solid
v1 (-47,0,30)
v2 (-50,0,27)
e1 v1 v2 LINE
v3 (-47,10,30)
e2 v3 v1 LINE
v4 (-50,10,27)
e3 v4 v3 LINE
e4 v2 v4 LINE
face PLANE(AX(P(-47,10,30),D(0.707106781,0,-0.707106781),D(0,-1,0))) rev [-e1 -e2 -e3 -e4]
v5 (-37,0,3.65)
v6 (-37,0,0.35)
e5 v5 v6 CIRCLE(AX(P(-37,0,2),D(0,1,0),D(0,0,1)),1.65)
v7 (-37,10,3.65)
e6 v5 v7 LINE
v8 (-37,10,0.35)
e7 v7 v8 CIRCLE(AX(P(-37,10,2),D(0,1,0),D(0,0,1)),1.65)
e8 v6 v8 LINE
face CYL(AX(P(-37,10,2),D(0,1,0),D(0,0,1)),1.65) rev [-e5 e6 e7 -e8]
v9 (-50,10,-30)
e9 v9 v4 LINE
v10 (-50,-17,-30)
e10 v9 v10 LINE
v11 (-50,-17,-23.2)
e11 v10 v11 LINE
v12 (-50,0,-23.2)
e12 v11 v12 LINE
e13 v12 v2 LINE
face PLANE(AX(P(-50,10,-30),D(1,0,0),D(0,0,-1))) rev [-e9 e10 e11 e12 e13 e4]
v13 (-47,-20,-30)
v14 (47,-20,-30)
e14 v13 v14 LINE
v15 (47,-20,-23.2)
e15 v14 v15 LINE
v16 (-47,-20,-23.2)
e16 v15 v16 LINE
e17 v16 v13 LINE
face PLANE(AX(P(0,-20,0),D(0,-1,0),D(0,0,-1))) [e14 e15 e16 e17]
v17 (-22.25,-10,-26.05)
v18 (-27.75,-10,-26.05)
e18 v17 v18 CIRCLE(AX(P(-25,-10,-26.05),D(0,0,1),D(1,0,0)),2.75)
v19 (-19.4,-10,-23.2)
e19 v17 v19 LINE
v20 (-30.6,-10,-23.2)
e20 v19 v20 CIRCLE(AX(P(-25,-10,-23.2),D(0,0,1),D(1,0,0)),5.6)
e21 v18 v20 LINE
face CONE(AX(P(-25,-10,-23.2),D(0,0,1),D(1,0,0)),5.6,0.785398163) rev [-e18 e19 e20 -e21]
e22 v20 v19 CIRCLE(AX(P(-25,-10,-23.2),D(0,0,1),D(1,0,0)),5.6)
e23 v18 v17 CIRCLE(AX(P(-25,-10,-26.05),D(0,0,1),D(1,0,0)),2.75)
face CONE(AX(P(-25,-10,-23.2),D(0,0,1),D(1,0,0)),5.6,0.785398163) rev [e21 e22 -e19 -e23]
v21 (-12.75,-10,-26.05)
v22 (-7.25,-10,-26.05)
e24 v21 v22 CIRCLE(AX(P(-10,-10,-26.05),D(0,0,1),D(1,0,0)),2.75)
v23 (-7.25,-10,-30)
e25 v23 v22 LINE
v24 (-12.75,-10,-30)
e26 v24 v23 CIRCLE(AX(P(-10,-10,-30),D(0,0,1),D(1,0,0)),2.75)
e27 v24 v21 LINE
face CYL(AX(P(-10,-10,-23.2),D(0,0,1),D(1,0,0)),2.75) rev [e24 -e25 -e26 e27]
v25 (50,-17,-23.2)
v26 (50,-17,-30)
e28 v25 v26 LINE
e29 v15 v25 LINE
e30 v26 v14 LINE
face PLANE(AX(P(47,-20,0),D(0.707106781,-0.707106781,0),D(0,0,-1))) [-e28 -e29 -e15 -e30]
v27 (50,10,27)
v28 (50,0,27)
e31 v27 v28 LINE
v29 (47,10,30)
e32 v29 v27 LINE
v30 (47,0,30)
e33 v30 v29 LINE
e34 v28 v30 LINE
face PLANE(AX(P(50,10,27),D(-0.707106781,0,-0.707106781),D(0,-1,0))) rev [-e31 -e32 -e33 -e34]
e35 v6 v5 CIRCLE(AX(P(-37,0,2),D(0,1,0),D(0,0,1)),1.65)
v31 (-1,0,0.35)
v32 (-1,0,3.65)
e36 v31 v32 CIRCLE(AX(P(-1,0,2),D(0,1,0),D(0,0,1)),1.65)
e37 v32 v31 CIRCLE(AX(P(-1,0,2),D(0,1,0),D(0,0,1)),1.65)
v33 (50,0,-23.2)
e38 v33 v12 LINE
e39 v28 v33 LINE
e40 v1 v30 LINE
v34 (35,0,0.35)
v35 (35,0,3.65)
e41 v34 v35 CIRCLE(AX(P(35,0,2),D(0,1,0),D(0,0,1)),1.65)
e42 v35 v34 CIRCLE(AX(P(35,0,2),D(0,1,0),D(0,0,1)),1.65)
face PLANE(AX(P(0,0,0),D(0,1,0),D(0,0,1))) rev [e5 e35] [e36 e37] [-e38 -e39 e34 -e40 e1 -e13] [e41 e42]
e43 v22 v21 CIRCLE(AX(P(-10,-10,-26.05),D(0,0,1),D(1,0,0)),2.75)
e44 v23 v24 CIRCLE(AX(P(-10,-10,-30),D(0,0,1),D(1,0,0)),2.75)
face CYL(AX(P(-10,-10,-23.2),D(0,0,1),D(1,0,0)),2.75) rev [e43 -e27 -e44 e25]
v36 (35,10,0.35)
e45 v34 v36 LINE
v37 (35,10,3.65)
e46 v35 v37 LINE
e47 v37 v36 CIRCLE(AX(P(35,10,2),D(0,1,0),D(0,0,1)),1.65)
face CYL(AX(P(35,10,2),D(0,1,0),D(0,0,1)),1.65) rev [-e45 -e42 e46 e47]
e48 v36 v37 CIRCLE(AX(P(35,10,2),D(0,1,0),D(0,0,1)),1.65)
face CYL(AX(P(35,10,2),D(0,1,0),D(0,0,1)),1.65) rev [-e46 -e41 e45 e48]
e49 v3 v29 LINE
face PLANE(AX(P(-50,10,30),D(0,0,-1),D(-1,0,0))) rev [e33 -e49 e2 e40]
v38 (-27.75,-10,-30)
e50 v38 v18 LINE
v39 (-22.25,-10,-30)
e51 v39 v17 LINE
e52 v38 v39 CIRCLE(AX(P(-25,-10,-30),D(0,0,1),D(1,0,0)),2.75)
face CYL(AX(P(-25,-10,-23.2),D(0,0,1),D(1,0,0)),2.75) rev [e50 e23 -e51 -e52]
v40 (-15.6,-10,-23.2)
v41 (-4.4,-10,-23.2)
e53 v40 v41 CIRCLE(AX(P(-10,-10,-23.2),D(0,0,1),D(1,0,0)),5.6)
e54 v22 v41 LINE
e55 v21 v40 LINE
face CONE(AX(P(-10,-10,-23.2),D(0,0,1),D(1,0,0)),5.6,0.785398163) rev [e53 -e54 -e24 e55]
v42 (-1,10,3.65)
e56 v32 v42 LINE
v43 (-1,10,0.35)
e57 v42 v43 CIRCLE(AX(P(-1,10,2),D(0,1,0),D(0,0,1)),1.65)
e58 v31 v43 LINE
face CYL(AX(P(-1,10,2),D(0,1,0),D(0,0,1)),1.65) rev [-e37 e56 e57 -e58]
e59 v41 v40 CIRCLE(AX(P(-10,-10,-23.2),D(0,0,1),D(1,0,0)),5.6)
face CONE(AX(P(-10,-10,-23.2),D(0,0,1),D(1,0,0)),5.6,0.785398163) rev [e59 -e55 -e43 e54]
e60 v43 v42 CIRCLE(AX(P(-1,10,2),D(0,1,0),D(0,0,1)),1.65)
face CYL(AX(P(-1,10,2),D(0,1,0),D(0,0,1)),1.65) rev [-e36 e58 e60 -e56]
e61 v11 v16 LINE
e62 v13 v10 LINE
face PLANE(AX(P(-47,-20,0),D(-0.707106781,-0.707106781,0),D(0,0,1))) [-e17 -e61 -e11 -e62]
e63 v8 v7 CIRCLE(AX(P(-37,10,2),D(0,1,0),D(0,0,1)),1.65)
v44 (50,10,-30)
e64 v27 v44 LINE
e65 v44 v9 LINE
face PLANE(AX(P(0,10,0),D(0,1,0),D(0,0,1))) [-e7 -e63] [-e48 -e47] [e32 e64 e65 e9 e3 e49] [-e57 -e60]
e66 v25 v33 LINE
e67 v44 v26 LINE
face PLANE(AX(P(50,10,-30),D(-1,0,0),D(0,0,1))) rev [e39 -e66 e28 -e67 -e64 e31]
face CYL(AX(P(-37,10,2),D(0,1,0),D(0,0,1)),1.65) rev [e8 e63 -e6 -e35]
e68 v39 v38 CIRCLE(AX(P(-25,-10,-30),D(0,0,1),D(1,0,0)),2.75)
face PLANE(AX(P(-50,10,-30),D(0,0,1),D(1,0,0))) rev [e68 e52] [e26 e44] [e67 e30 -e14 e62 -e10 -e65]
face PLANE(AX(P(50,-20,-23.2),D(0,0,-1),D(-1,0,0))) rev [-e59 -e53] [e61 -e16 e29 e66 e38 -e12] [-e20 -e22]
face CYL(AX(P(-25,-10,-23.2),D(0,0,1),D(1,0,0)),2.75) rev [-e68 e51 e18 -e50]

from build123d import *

# Parameters (mm, degrees)
SKETCH_1_W                = 100
SKETCH_1_H                = 60
EXTRUDE_1_DEPTH           = 10
SKETCH_2_W                = 100
SKETCH_2_H                = 6.8
EXTRUDE_2_DEPTH           = 20
CHAMFER_1_SIZE            = 3
HOLE_WIZARD_M4_1_D        = 3.3
HOLE_WIZARD_M4_1_DEPTH    = 10.1
HOLE_WIZARD_M4_1_TIP      = 0.991420021
HOLE_WIZARD_1_D           = 5.5
HOLE_WIZARD_1_DEPTH       = 10.1
HOLE_WIZARD_1_CSINK_D     = 11.2
HOLE_WIZARD_1_CSINK_ANGLE = 90
HOLE_WIZARD_1_TIP         = 1.652366702


with BuildPart() as part:
    # 草图1 → 凸台-拉伸1 (new body)
    with BuildSketch(Plane(origin=(0, 0, 0), x_dir=(1, 0, 0), z_dir=(0, 1, 0))):
        Rectangle(SKETCH_1_W, SKETCH_1_H)
    extrude(amount=EXTRUDE_1_DEPTH)

    # 草图2 → 凸台-拉伸2 (add)
    with BuildSketch(Plane.XZ):
        with Locations((0, -26.6)):
            Rectangle(SKETCH_2_W, SKETCH_2_H)
    extrude(amount=EXTRUDE_2_DEPTH)

    # 倒角1
    chamfer_1_edges = [part.edges().sort_by_distance(p)[0] for p in [
        (50, -20, -26.6),
        (-50, -20, -26.6),
        (50, 5, 30),
        (-50, 5, 30),
    ]]
    chamfer(chamfer_1_edges, length=CHAMFER_1_SIZE)

    # M4 螺纹孔1
    with Locations(Plane(origin=(0, 10, 0), x_dir=(1, 0, 0), z_dir=(0, 1, 0))):
        with Locations((35, -2), (-37, -2), (-1, -2)):
            Hole(HOLE_WIZARD_M4_1_D / 2, depth=HOLE_WIZARD_M4_1_DEPTH)
            with Locations((0, 0, -(HOLE_WIZARD_M4_1_DEPTH + HOLE_WIZARD_M4_1_TIP / 2))):  # 118° drill point
                Cone(0, HOLE_WIZARD_M4_1_D / 2, HOLE_WIZARD_M4_1_TIP, mode=Mode.SUBTRACT)

    # 打孔尺寸(%根据)开槽半沉头木螺钉的类型1
    with Locations(Plane.XY.offset(-23.2)):
        with Locations((-10, -10), (-25, -10)):
            CounterSinkHole(HOLE_WIZARD_1_D / 2, HOLE_WIZARD_1_CSINK_D / 2, depth=HOLE_WIZARD_1_DEPTH, counter_sink_angle=HOLE_WIZARD_1_CSINK_ANGLE)
            with Locations((0, 0, -(HOLE_WIZARD_1_DEPTH + HOLE_WIZARD_1_TIP / 2))):  # 118° drill point
                Cone(0, HOLE_WIZARD_1_D / 2, HOLE_WIZARD_1_TIP, mode=Mode.SUBTRACT)


solid = part.part
